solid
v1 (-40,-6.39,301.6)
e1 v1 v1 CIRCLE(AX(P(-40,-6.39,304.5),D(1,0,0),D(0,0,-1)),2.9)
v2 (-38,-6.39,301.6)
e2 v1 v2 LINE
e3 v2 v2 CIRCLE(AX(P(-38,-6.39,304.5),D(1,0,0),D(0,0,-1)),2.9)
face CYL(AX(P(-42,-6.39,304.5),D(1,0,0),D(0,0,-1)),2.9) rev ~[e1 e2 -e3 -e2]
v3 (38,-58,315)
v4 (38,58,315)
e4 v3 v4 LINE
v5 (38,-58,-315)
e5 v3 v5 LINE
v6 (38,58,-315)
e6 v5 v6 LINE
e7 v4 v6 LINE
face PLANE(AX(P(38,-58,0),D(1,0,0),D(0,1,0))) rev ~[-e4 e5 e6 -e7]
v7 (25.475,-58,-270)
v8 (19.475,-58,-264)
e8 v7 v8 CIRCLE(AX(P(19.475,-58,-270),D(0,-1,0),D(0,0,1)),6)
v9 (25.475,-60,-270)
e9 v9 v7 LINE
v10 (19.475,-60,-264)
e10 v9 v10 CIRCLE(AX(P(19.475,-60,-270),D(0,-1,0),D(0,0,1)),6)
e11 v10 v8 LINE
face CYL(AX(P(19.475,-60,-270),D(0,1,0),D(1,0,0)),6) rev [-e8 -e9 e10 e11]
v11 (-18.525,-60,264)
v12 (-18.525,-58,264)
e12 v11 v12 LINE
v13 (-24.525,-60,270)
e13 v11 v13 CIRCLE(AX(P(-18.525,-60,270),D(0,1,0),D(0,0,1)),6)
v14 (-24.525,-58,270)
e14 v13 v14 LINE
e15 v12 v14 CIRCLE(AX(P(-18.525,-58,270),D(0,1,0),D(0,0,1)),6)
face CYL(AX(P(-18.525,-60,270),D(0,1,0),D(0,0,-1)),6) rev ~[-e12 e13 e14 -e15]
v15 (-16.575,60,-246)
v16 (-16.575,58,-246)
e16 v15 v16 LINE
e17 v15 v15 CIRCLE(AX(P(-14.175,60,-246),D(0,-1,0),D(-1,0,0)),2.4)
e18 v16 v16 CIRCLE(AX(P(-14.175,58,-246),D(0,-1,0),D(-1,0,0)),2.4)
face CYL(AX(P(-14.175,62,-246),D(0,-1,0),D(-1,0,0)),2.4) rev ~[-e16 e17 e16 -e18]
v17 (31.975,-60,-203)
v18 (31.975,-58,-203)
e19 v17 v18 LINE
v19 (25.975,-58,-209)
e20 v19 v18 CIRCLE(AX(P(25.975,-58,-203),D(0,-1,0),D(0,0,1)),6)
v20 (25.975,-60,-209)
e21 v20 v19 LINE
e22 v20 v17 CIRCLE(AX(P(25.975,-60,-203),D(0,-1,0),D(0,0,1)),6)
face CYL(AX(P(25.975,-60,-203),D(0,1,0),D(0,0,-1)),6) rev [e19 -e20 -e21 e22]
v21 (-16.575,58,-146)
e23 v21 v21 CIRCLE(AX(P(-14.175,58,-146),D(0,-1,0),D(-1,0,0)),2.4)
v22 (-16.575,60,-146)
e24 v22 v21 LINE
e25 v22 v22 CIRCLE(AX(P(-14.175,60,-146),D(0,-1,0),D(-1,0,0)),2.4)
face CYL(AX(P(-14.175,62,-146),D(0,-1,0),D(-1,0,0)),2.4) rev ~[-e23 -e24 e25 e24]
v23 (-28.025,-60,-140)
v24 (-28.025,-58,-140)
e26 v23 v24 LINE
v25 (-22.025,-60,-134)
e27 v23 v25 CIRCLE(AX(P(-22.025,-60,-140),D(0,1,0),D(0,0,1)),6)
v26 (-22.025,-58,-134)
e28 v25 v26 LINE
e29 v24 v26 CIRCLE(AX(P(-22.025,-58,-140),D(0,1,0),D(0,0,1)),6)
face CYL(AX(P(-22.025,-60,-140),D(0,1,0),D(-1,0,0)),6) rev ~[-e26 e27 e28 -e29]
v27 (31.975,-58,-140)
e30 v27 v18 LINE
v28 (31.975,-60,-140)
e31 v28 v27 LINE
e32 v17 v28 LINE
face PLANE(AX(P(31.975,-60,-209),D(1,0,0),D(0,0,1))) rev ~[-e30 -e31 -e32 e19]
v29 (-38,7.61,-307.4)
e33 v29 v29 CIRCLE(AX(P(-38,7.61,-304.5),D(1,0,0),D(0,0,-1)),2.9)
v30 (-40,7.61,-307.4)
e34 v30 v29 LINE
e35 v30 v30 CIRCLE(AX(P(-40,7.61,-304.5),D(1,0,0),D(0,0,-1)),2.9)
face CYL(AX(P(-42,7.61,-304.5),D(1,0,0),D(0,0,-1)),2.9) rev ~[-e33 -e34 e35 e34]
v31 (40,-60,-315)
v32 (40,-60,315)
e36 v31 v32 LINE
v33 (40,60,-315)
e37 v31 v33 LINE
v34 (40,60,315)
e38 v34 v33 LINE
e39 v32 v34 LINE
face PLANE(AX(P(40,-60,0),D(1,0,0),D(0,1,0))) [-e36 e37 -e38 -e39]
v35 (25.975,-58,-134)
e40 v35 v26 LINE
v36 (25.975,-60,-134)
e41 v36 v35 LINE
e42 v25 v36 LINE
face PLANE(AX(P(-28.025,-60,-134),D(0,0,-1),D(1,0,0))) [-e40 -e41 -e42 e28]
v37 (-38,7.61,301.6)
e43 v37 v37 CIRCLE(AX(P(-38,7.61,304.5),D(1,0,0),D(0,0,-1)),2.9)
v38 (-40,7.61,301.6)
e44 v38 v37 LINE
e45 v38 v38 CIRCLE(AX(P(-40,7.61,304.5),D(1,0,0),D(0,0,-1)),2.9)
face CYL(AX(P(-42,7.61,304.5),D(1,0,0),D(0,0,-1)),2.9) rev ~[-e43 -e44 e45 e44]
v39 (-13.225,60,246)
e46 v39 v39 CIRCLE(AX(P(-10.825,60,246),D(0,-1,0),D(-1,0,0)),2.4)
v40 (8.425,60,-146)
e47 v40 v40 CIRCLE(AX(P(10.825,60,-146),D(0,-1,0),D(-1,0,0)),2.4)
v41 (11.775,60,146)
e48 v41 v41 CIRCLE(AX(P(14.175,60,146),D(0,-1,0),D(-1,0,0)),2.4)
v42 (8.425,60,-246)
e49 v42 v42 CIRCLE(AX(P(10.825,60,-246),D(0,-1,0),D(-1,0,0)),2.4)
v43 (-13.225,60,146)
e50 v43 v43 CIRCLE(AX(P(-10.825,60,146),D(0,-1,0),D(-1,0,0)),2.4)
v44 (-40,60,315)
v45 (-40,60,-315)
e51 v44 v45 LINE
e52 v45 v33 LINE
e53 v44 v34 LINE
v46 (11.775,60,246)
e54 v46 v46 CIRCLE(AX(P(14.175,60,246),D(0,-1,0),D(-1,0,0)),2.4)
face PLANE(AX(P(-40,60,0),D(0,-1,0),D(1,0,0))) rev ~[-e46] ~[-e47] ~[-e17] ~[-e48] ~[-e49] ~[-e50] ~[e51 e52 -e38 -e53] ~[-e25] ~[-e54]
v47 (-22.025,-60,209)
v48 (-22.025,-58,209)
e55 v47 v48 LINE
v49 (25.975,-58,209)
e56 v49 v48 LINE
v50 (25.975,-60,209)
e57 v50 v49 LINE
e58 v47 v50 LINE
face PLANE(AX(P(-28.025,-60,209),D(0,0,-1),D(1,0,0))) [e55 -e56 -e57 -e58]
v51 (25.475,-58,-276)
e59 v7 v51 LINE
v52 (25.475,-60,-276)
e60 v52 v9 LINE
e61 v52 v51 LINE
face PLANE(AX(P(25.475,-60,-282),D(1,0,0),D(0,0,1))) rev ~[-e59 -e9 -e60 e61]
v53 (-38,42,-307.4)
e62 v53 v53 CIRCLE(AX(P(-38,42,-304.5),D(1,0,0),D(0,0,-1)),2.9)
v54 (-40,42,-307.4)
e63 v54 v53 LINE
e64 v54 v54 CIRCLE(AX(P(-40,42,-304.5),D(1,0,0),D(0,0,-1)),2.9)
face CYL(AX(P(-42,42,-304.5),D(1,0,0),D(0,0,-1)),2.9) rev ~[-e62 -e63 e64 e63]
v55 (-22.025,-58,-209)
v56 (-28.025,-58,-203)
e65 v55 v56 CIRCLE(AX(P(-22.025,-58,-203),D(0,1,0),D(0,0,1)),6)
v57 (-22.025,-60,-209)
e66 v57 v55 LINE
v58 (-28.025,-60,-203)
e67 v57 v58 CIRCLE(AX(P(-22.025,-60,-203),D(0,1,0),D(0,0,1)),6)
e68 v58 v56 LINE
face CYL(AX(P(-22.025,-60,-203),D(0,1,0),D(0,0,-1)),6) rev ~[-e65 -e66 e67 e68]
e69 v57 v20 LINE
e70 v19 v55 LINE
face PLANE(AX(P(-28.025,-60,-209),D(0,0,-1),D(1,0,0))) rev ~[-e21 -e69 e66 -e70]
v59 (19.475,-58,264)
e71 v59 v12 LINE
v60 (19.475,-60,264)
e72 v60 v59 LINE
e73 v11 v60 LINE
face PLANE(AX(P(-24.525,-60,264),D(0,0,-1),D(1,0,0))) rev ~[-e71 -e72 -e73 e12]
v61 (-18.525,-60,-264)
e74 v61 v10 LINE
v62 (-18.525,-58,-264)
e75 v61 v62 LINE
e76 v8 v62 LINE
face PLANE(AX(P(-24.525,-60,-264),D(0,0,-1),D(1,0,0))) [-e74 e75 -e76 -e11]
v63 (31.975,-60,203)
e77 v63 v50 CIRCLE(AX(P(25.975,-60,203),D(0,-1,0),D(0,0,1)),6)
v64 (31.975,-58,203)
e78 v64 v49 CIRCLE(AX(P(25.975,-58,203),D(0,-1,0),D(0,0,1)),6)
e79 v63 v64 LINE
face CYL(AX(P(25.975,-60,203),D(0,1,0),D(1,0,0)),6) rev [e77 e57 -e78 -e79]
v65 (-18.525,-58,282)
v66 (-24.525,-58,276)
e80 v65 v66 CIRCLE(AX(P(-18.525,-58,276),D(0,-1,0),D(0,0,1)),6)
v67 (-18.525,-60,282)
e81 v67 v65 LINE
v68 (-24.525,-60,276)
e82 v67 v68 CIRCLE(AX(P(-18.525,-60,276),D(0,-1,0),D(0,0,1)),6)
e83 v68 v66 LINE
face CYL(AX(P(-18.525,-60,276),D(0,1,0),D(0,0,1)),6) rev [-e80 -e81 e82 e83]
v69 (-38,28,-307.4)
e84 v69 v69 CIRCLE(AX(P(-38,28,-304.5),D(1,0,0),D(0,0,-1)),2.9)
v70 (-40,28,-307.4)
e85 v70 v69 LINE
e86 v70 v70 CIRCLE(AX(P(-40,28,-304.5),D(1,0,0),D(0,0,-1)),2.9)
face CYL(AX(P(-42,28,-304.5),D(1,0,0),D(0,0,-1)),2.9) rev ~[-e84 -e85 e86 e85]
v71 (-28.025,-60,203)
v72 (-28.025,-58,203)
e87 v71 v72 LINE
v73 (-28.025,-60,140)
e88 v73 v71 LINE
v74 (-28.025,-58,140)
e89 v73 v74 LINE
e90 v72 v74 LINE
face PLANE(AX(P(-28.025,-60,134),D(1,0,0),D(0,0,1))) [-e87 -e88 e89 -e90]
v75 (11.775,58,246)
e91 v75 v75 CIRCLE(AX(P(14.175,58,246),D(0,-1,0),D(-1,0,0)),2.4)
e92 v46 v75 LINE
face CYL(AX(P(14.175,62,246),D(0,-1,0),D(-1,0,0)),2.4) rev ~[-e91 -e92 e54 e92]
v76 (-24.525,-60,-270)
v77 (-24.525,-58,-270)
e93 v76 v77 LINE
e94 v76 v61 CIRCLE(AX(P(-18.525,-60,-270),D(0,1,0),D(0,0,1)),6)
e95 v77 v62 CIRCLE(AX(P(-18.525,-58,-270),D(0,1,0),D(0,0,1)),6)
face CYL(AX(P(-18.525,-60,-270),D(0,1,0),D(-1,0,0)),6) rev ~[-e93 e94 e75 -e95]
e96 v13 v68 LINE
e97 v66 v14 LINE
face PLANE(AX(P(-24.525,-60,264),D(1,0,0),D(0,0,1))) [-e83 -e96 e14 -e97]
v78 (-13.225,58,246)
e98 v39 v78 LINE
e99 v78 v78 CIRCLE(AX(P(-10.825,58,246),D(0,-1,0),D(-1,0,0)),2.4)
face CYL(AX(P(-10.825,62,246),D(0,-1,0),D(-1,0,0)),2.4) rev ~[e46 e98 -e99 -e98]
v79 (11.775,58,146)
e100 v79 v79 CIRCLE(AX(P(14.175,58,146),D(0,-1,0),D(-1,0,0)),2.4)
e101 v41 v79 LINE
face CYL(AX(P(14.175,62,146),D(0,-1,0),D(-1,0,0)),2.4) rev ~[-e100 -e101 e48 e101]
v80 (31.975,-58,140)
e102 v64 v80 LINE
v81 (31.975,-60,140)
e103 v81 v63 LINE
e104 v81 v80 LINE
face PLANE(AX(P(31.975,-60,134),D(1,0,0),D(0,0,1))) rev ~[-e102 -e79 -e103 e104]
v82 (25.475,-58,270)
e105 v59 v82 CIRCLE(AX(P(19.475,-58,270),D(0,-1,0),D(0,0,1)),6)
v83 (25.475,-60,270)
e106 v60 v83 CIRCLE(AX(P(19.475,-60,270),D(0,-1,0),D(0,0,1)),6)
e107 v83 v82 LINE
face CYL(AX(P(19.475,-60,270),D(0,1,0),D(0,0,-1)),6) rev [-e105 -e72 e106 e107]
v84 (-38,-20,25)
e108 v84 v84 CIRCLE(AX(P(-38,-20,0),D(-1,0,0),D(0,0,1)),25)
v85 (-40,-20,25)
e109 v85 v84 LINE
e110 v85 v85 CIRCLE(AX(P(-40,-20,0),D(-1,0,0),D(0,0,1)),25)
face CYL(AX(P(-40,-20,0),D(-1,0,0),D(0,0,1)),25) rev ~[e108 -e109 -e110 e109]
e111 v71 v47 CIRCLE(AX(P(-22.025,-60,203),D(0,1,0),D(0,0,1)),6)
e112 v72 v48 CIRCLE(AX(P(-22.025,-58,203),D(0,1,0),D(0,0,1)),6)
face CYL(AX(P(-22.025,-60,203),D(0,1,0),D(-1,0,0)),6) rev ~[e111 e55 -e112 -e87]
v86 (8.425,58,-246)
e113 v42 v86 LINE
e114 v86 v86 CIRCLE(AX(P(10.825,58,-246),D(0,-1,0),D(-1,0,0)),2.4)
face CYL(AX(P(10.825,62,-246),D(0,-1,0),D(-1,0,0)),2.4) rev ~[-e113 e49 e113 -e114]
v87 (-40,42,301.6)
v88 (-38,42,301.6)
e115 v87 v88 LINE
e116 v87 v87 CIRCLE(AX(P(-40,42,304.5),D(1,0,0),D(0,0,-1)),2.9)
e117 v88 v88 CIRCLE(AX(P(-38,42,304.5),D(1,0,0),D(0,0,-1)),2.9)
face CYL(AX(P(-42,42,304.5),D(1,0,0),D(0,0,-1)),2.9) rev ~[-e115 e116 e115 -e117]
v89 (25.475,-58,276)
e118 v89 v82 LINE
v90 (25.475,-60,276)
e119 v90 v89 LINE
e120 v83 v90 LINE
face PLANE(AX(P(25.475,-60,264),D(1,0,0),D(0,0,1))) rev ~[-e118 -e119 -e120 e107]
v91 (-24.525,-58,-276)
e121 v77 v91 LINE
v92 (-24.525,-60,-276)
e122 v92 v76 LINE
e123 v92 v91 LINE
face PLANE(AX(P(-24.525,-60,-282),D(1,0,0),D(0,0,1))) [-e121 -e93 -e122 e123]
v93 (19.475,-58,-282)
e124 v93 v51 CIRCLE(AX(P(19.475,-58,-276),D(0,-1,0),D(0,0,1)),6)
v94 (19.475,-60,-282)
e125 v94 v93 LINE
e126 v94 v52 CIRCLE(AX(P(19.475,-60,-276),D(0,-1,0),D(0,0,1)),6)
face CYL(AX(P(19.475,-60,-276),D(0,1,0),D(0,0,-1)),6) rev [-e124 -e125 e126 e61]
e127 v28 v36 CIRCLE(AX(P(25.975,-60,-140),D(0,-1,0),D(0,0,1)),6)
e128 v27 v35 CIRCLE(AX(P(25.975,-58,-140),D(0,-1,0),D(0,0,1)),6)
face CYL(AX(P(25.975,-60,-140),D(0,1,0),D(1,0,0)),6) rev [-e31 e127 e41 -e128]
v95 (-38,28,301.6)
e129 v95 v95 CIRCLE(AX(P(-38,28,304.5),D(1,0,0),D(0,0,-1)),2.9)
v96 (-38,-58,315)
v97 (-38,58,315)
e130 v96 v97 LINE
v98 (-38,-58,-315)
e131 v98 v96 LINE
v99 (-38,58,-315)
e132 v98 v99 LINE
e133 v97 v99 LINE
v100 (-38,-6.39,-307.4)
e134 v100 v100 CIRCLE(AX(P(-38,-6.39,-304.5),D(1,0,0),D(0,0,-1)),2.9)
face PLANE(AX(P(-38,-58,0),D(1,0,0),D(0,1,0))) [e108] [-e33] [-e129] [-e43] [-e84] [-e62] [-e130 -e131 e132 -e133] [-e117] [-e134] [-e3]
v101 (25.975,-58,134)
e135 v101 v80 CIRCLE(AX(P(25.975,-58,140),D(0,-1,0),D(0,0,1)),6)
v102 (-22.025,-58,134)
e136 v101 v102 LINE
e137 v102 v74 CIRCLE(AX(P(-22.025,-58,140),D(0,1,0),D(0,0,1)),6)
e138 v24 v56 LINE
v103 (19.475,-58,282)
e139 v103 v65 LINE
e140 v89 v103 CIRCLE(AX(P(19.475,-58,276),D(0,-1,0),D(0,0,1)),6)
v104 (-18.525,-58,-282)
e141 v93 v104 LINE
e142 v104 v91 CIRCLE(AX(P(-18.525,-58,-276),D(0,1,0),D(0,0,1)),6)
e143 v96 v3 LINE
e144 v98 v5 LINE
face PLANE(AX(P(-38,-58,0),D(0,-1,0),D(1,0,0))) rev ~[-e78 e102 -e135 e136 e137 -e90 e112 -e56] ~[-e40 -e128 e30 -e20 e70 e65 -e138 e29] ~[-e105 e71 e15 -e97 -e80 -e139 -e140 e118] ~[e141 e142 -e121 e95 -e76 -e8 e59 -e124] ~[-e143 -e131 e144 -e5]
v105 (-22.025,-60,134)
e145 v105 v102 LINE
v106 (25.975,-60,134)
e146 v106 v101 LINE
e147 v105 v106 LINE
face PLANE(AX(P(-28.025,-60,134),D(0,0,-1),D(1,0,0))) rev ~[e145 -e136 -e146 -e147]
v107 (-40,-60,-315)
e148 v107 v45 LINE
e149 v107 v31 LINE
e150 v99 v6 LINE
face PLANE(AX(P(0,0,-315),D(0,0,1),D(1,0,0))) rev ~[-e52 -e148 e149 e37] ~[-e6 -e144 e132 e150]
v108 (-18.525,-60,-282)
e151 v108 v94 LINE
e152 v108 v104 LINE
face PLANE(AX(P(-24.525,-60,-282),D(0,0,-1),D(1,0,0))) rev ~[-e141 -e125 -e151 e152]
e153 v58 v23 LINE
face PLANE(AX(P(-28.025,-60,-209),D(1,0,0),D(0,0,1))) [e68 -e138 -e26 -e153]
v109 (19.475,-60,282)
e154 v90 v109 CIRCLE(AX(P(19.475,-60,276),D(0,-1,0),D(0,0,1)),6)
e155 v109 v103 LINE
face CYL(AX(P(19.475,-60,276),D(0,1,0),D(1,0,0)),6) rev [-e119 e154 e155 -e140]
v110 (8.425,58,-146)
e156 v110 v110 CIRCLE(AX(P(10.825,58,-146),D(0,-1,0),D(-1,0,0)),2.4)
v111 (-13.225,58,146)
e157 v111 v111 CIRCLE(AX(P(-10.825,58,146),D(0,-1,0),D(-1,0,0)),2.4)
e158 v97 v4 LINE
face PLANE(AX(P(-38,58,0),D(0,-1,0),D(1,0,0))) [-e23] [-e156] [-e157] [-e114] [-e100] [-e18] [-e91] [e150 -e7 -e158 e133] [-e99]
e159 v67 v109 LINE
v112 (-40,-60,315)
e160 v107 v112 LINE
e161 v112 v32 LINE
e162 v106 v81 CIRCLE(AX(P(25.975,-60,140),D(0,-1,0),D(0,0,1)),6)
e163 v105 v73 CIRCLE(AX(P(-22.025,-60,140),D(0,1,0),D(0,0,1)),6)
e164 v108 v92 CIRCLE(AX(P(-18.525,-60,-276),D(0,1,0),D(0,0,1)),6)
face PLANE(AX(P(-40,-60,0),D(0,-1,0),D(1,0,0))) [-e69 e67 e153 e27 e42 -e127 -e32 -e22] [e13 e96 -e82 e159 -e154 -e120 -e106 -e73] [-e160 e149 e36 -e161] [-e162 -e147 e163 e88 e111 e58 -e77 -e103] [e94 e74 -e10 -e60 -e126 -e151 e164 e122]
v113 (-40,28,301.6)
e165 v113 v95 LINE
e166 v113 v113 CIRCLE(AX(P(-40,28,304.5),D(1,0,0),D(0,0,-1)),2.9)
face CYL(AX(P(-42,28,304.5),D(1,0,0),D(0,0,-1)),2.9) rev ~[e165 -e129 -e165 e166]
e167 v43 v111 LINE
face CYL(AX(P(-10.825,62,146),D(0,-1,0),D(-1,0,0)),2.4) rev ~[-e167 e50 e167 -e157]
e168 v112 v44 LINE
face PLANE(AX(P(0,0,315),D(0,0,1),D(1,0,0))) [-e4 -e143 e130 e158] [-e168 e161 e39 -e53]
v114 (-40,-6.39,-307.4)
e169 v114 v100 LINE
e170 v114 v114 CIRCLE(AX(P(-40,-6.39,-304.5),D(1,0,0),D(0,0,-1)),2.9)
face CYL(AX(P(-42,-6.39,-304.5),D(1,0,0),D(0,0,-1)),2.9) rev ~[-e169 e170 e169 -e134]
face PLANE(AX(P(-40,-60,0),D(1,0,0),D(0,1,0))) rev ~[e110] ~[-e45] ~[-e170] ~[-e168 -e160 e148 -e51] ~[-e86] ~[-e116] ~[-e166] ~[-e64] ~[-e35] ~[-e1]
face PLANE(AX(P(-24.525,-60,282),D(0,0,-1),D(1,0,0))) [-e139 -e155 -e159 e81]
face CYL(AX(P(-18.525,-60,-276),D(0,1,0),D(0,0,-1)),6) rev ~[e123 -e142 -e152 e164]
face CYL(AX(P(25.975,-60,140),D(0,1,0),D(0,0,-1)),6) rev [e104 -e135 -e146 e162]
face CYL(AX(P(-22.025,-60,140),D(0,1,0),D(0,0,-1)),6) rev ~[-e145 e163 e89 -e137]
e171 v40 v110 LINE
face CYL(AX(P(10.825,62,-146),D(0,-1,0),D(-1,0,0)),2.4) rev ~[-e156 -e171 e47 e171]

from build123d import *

# Parameters (mm, degrees)
SKETCH_1_W             = 80
SKETCH_1_H             = 120
SKETCH_1_W_2           = 76
SKETCH_1_H_2           = 116
EXTRUDE_1_DEPTH        = 315
CUT_EXTRUDE_2_REACH    = 332.492
SKETCH_4_R             = 25
HOLE_WIZARD_M5_1_D     = 5.8
HOLE_WIZARD_M5_1_DEPTH = 2
HOLE_WIZARD_M4_1_D     = 4.8
HOLE_WIZARD_M4_1_DEPTH = 2
CUT_EXTRUDE_3_REACH    = 341.448
SKETCH_15_W            = 50
SKETCH_15_H            = 18
SKETCH_15_W_2          = 60
SKETCH_15_H_2          = 75
FILLET_1_R             = 6


with BuildPart() as part:
    # 草图1 → 拉伸-薄壁1 (new, symmetric)
    with BuildSketch(Plane.XY):
        Rectangle(SKETCH_1_W, SKETCH_1_H)
        Rectangle(SKETCH_1_W_2, SKETCH_1_H_2, mode=Mode.SUBTRACT)
    extrude(amount=EXTRUDE_1_DEPTH, both=True)

    # 草图4 → 切除-拉伸2 (cut, up to next)
    with BuildSketch(Plane.ZY.offset(40), mode=Mode.PRIVATE) as cut_extrude_2_sk1:
        with Locations((0, -20)):
            Circle(SKETCH_4_R)
    cut_extrude_2_tool1 = extrude(cut_extrude_2_sk1.sketch, amount=-CUT_EXTRUDE_2_REACH, mode=Mode.PRIVATE) & part.part
    add(cut_extrude_2_tool1.solids().sort_by_distance((-40, -20, 0))[0], mode=Mode.SUBTRACT)

    # M5 间隙孔1
    with Locations(Plane.ZY.offset(40)):
        with Locations((304.5, 42), (304.5, 28), (304.5, 7.61), (304.5, -6.39), (-304.5, -6.39), (-304.5, 7.61), (-304.5, 28), (-304.5, 42)):
            Hole(HOLE_WIZARD_M5_1_D / 2, depth=HOLE_WIZARD_M5_1_DEPTH)

    # M4 间隙孔1
    with Locations(Plane(origin=(0, 60, 0), x_dir=(1, 0, 0), z_dir=(0, 1, 0))):
        with Locations((-14.175, 246), (10.825, 246), (-14.175, 146), (10.825, 146), (-10.825, -146), (14.175, -146), (-10.825, -246), (14.175, -246)):
            Hole(HOLE_WIZARD_M4_1_D / 2, depth=HOLE_WIZARD_M4_1_DEPTH)

    # 草图15 → 切除-拉伸3 (cut, up to next)
    with BuildSketch(Plane.XZ.offset(60), mode=Mode.PRIVATE) as cut_extrude_3_sk1:
        with Locations((0.475, -273)):
            Rectangle(SKETCH_15_W, SKETCH_15_H)
    cut_extrude_3_tool1 = extrude(cut_extrude_3_sk1.sketch, amount=-CUT_EXTRUDE_3_REACH, mode=Mode.PRIVATE) & part.part
    # 草图15 → 切除-拉伸3 (cut, up to next)
    with BuildSketch(Plane.XZ.offset(60), mode=Mode.PRIVATE) as cut_extrude_3_sk2:
        with Locations((1.975, -171.5)):
            Rectangle(SKETCH_15_W_2, SKETCH_15_H_2)
    cut_extrude_3_tool2 = extrude(cut_extrude_3_sk2.sketch, amount=-CUT_EXTRUDE_3_REACH, mode=Mode.PRIVATE) & part.part
    # 草图15 → 切除-拉伸3 (cut, up to next)
    with BuildSketch(Plane.XZ.offset(60), mode=Mode.PRIVATE) as cut_extrude_3_sk3:
        with Locations((1.975, 171.5)):
            Rectangle(SKETCH_15_W_2, SKETCH_15_H_2)
    cut_extrude_3_tool3 = extrude(cut_extrude_3_sk3.sketch, amount=-CUT_EXTRUDE_3_REACH, mode=Mode.PRIVATE) & part.part
    # 草图15 → 切除-拉伸3 (cut, up to next)
    with BuildSketch(Plane.XZ.offset(60), mode=Mode.PRIVATE) as cut_extrude_3_sk4:
        with Locations((0.475, 273)):
            Rectangle(SKETCH_15_W, SKETCH_15_H)
    cut_extrude_3_tool4 = extrude(cut_extrude_3_sk4.sketch, amount=-CUT_EXTRUDE_3_REACH, mode=Mode.PRIVATE) & part.part
    add(cut_extrude_3_tool1.solids().sort_by_distance((0.475, -60, -273))[0], mode=Mode.SUBTRACT)
    add(cut_extrude_3_tool2.solids().sort_by_distance((1.975, -60, -171.5))[0], mode=Mode.SUBTRACT)
    add(cut_extrude_3_tool3.solids().sort_by_distance((1.975, -60, 171.5))[0], mode=Mode.SUBTRACT)
    add(cut_extrude_3_tool4.solids().sort_by_distance((0.475, -60, 273))[0], mode=Mode.SUBTRACT)

    # 圆角1
    fillet_1_edges = [part.edges().sort_by_distance(p)[0] for p in [
        (25.475, -59, -282),
        (25.475, -59, -264),
        (-24.525, -59, -264),
        (-24.525, -59, -282),
        (-28.025, -59, 134),
        (31.975, -59, 134),
        (31.975, -59, 209),
        (-28.025, -59, 209),
        (-24.525, -59, 282),
        (-24.525, -59, 264),
        (25.475, -59, 264),
        (25.475, -59, 282),
        (31.975, -59, -209),
        (31.975, -59, -134),
        (-28.025, -59, -134),
        (-28.025, -59, -209),
    ]]
    fillet(fillet_1_edges, radius=FILLET_1_R)


solid = part.part
